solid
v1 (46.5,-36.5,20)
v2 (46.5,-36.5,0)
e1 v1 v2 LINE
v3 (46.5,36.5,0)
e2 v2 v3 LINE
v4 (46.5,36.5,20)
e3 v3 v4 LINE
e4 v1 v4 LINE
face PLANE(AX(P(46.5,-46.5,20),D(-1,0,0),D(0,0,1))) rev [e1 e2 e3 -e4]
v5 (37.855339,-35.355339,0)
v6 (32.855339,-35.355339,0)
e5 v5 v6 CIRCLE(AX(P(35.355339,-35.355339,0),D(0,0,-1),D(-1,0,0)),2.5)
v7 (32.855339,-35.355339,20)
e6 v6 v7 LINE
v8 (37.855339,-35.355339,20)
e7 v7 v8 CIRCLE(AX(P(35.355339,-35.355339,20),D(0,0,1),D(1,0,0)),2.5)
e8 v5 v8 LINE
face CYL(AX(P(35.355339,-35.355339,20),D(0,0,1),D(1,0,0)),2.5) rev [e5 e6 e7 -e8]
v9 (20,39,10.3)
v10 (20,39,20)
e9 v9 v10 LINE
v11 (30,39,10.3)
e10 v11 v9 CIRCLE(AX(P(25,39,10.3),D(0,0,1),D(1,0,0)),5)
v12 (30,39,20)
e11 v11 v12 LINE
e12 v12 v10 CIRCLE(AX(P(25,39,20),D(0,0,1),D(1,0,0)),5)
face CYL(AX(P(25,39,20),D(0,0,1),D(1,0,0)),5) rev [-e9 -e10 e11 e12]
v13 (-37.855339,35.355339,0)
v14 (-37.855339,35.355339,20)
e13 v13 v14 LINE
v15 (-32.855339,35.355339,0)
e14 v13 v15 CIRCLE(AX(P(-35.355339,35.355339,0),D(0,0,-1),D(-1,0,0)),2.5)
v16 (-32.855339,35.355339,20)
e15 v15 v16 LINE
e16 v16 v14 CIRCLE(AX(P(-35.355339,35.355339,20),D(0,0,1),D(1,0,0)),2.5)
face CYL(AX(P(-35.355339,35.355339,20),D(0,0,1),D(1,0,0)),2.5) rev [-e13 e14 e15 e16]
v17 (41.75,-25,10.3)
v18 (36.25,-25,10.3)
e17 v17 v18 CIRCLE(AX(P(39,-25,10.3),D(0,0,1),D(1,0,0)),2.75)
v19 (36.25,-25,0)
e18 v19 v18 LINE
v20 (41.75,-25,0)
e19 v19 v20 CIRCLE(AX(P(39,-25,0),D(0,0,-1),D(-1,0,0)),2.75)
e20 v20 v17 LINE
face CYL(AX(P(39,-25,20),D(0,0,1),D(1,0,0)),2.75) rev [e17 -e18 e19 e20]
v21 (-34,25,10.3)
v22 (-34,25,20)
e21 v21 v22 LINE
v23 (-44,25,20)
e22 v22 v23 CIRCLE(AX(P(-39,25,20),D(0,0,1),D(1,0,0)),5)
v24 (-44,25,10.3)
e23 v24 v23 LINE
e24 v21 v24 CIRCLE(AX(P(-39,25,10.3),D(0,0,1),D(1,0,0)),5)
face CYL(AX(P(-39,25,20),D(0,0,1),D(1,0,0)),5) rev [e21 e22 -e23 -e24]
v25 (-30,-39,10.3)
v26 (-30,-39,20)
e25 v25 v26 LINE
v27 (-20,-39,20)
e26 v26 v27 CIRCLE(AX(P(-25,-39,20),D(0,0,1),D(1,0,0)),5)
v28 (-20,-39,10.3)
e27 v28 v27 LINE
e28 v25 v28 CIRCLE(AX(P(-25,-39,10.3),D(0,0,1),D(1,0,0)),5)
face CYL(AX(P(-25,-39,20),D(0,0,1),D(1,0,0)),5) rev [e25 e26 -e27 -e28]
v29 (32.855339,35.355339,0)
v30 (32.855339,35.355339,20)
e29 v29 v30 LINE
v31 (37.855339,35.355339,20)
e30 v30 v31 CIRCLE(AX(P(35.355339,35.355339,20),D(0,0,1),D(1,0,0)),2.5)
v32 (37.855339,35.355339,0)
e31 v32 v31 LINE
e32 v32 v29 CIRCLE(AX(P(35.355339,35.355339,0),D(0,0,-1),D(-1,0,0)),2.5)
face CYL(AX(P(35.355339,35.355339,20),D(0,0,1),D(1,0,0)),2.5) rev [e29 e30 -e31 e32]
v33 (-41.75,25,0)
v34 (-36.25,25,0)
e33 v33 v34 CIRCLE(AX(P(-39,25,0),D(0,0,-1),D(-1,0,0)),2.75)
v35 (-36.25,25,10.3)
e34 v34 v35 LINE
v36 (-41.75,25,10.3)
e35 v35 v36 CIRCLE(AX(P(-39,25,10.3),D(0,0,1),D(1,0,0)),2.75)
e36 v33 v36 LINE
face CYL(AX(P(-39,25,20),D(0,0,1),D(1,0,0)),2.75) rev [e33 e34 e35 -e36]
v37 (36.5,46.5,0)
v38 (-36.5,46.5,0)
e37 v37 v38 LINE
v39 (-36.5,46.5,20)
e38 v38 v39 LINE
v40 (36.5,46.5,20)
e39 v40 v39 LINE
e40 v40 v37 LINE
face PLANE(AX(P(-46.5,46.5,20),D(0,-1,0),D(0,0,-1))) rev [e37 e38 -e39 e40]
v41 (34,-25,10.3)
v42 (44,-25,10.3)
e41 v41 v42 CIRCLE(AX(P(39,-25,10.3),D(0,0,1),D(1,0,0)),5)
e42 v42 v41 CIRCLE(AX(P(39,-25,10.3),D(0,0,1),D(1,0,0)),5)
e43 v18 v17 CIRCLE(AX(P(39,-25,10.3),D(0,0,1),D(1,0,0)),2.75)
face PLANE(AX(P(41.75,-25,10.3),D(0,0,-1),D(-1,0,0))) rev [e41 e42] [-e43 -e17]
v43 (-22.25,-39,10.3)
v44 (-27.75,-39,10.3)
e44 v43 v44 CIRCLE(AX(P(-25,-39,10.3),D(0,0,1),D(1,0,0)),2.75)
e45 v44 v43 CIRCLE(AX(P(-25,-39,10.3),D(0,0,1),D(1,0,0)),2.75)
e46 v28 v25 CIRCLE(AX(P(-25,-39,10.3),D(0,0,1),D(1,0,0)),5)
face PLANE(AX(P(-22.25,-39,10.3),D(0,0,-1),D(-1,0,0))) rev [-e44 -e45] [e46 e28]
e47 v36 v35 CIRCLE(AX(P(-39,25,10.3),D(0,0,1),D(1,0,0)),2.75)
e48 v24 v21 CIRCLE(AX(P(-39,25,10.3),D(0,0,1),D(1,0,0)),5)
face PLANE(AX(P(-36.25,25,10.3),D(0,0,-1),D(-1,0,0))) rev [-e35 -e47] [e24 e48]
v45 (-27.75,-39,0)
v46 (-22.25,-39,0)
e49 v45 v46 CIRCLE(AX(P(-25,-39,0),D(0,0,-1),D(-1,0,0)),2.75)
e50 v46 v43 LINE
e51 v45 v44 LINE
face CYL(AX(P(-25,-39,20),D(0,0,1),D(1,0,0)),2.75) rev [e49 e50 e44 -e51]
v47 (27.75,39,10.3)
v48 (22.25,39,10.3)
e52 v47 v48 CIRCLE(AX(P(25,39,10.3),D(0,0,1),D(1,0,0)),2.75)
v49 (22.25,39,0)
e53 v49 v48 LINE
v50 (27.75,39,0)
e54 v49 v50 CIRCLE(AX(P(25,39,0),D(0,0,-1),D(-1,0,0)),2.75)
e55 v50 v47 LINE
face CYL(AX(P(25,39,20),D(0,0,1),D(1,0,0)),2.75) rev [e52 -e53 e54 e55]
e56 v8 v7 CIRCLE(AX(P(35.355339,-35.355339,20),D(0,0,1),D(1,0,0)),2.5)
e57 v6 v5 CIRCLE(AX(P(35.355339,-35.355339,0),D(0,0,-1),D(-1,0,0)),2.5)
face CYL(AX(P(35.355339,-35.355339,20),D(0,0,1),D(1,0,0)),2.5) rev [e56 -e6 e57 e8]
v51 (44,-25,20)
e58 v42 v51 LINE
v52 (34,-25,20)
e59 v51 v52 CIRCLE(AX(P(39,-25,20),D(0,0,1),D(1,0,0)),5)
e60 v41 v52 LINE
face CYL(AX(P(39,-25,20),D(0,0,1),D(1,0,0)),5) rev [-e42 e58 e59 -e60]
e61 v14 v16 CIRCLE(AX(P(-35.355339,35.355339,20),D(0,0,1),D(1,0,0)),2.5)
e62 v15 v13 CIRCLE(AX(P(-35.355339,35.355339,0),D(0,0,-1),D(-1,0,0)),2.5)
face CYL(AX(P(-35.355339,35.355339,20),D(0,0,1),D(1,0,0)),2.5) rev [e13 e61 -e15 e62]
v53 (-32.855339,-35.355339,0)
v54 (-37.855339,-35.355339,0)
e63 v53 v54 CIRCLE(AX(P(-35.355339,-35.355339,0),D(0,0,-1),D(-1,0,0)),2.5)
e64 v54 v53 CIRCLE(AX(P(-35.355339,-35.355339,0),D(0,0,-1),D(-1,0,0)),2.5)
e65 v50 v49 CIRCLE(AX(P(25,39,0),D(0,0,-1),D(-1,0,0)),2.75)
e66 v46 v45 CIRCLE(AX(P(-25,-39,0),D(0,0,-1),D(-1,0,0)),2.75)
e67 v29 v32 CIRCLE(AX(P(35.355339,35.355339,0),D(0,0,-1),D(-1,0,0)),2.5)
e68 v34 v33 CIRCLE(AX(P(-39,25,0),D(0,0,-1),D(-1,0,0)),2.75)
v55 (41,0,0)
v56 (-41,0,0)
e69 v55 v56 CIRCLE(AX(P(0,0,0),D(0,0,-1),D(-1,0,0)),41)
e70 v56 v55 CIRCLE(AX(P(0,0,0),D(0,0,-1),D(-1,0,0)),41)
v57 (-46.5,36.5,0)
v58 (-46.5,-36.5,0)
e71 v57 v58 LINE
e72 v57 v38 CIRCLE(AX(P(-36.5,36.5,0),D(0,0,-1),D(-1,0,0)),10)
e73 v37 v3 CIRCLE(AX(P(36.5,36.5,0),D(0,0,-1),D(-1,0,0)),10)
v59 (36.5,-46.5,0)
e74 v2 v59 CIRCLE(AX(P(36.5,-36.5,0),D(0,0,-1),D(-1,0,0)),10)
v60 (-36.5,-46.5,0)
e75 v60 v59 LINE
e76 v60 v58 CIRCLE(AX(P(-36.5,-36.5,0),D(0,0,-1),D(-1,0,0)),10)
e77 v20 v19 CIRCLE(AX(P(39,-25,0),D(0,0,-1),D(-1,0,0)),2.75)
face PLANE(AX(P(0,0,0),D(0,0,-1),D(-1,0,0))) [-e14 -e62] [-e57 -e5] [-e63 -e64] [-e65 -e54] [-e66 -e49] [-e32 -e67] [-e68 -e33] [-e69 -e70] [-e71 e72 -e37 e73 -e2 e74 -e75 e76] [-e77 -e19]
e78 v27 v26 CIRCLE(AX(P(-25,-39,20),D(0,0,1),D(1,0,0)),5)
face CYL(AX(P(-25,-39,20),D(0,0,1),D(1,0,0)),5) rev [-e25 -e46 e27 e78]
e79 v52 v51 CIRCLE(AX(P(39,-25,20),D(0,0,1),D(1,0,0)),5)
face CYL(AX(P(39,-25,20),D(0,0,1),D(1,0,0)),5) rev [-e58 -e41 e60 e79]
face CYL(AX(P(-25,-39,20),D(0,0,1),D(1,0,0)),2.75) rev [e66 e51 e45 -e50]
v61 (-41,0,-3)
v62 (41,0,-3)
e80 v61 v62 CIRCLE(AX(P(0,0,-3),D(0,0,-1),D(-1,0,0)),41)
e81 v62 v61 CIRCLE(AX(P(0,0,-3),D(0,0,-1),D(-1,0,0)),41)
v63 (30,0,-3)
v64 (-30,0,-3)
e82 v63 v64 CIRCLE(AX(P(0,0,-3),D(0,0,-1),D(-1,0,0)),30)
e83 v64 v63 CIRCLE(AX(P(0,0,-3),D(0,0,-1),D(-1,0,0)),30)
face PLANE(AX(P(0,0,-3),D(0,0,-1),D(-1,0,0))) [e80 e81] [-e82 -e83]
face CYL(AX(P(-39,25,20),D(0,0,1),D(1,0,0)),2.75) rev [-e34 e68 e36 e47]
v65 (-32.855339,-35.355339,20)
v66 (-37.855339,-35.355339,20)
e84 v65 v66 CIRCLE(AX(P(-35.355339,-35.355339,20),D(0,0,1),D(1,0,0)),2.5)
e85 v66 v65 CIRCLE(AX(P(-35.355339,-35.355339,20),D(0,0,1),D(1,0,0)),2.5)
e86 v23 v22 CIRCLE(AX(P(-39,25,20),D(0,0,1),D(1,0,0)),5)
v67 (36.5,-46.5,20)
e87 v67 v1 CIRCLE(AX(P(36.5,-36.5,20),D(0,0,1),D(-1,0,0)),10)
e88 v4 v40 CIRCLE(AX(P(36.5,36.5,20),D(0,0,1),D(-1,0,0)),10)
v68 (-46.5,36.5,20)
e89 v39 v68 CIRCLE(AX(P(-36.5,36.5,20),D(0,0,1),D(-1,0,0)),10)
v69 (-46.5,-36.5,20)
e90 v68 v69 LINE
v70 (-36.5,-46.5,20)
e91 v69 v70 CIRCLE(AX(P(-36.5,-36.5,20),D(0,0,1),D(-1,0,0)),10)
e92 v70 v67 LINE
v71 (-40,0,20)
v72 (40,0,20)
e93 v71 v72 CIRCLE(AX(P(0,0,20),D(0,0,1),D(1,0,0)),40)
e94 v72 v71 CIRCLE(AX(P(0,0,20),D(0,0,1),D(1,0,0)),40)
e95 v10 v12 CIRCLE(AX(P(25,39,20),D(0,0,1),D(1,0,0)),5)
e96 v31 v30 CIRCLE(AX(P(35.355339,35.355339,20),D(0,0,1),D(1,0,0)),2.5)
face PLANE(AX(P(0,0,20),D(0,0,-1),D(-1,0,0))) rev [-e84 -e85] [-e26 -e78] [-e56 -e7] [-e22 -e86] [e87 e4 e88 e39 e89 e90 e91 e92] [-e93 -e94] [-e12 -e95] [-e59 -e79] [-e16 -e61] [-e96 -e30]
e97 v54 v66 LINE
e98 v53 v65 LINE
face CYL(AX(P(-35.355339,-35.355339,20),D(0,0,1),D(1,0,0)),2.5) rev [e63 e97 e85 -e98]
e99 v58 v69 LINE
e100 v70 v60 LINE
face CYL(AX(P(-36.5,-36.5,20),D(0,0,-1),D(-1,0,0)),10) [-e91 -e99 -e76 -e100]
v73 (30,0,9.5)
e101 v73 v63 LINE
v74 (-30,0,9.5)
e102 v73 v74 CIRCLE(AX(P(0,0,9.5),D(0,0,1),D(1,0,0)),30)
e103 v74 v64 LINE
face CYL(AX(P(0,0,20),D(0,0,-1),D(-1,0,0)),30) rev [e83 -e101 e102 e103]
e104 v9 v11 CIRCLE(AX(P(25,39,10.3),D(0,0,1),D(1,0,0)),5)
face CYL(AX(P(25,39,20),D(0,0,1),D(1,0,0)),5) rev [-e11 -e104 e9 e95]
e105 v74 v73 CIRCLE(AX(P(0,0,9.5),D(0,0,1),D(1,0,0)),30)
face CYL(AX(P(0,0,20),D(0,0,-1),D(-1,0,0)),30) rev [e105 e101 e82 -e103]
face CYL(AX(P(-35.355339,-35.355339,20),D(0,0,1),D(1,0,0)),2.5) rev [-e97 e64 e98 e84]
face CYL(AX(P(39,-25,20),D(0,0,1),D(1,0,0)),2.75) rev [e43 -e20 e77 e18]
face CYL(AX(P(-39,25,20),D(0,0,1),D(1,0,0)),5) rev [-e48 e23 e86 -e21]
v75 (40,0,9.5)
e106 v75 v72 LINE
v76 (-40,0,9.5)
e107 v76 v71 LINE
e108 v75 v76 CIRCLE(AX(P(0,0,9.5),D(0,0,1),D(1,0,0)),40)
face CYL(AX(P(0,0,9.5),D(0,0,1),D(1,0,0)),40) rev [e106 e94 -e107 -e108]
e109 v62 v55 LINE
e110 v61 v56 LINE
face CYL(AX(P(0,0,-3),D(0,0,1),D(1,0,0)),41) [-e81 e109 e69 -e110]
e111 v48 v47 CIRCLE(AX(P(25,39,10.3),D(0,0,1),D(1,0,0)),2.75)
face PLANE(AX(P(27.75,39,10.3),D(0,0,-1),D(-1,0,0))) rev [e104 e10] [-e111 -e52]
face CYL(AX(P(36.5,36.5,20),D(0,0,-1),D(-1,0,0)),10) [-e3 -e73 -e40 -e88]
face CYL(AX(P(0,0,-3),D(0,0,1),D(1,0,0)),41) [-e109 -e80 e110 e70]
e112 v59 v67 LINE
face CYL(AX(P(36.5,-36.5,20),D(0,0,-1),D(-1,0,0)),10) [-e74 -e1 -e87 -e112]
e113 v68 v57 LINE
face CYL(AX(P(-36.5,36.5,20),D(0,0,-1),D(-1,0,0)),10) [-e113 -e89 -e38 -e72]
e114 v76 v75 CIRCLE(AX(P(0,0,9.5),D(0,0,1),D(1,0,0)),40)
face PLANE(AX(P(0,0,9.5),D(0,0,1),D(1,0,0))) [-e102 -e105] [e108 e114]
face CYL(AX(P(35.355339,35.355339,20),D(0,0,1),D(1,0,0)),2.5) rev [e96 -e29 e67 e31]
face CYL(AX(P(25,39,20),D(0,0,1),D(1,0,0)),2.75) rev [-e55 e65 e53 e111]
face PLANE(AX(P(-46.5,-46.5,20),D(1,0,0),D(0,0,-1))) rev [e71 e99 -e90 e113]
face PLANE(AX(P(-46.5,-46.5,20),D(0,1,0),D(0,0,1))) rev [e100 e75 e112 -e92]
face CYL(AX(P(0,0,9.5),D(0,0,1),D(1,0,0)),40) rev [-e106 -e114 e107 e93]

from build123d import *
from build123d.topology import SkipClean

# Parameters (mm, degrees)
SKETCH1_W                                           = 93
SKETCH1_H                                           = 93
SKETCH1_R                                           = 30
BOSS_EXTRUDE1_DEPTH                                 = 20
FILLET1_R                                           = 10
BOSS_EXTRUDE2_START                                 = 3
SKETCH6_R                                           = 41
SKETCH6_R_2                                         = 30
BOSS_EXTRUDE2_DEPTH                                 = 3
SKETCH7_R                                           = 40
CUT_EXTRUDE1_DEPTH                                  = 10.5
M6_TAPPED_HOLE1_D                                   = 5
HOLE_SPEC_PER_SOCKET_HEAD_CAP_SCREW_TYP_D           = 5.5
HOLE_SPEC_PER_SOCKET_HEAD_CAP_SCREW_TYP_CBORE_D     = 10
HOLE_SPEC_PER_SOCKET_HEAD_CAP_SCREW_TYP_CBORE_DEPTH = 9.7
CIRPATTERN2_COUNT                                   = 4


with BuildPart() as part:
    # Sketch1 → Boss-Extrude1 (new body)
    with BuildSketch(Plane.XY):
        Rectangle(SKETCH1_W, SKETCH1_H)
        Circle(SKETCH1_R, mode=Mode.SUBTRACT)
    extrude(amount=BOSS_EXTRUDE1_DEPTH)

    # Fillet1
    fillet1_edges = [part.edges().sort_by_distance(p)[0] for p in [
        (46.5, -46.5, 10),
        (-46.5, -46.5, 10),
        (-46.5, 46.5, 10),
        (46.5, 46.5, 10),
    ]]
    fillet(fillet1_edges, radius=FILLET1_R)

    # Sketch6 → Boss-Extrude2 (add)
    with SkipClean():  # the faces are left unmerged after this step: merging them gives an invalid solid
        with BuildSketch(Plane(origin=(0, 0, 0), x_dir=(-1, 0, 0), z_dir=(0, 0, -1)).offset(BOSS_EXTRUDE2_START)):
            Circle(SKETCH6_R)
            Circle(SKETCH6_R_2, mode=Mode.SUBTRACT)
        extrude(amount=-BOSS_EXTRUDE2_DEPTH)

    # Sketch7 → Cut-Extrude1 (cut)
    with BuildSketch(Plane.XY.offset(20)):
        Circle(SKETCH7_R)
    extrude(amount=-CUT_EXTRUDE1_DEPTH, mode=Mode.SUBTRACT)

    # M6 Tapped Hole1 (through all)
    with Locations(Plane.XY.offset(20)):
        with Locations((-35.355339059, 35.355339059), (35.355339059, 35.355339059), (35.355339059, -35.355339059), (-35.355339059, -35.355339059)):
            Hole(M6_TAPPED_HOLE1_D / 2)

    # Hole Spec (per socket head cap screw type) 1 (through all)
    with Locations(Plane.XY.offset(20)):
        with Locations((-25, -39)):
            hole_spec_per_socket_head_cap_screw_typ = CounterBoreHole(HOLE_SPEC_PER_SOCKET_HEAD_CAP_SCREW_TYP_D / 2, HOLE_SPEC_PER_SOCKET_HEAD_CAP_SCREW_TYP_CBORE_D / 2, HOLE_SPEC_PER_SOCKET_HEAD_CAP_SCREW_TYP_CBORE_DEPTH)

    # CirPattern2: Hole Spec (per socket head cap screw type) 1 ×4 about axis
    cirpattern2_axis = Axis((0, 0, 0), (0, 0, 1))
    for i in range(1, CIRPATTERN2_COUNT):
        add(hole_spec_per_socket_head_cap_screw_typ.rotate(cirpattern2_axis, i * 360 / CIRPATTERN2_COUNT), mode=Mode.SUBTRACT)


solid = part.part
